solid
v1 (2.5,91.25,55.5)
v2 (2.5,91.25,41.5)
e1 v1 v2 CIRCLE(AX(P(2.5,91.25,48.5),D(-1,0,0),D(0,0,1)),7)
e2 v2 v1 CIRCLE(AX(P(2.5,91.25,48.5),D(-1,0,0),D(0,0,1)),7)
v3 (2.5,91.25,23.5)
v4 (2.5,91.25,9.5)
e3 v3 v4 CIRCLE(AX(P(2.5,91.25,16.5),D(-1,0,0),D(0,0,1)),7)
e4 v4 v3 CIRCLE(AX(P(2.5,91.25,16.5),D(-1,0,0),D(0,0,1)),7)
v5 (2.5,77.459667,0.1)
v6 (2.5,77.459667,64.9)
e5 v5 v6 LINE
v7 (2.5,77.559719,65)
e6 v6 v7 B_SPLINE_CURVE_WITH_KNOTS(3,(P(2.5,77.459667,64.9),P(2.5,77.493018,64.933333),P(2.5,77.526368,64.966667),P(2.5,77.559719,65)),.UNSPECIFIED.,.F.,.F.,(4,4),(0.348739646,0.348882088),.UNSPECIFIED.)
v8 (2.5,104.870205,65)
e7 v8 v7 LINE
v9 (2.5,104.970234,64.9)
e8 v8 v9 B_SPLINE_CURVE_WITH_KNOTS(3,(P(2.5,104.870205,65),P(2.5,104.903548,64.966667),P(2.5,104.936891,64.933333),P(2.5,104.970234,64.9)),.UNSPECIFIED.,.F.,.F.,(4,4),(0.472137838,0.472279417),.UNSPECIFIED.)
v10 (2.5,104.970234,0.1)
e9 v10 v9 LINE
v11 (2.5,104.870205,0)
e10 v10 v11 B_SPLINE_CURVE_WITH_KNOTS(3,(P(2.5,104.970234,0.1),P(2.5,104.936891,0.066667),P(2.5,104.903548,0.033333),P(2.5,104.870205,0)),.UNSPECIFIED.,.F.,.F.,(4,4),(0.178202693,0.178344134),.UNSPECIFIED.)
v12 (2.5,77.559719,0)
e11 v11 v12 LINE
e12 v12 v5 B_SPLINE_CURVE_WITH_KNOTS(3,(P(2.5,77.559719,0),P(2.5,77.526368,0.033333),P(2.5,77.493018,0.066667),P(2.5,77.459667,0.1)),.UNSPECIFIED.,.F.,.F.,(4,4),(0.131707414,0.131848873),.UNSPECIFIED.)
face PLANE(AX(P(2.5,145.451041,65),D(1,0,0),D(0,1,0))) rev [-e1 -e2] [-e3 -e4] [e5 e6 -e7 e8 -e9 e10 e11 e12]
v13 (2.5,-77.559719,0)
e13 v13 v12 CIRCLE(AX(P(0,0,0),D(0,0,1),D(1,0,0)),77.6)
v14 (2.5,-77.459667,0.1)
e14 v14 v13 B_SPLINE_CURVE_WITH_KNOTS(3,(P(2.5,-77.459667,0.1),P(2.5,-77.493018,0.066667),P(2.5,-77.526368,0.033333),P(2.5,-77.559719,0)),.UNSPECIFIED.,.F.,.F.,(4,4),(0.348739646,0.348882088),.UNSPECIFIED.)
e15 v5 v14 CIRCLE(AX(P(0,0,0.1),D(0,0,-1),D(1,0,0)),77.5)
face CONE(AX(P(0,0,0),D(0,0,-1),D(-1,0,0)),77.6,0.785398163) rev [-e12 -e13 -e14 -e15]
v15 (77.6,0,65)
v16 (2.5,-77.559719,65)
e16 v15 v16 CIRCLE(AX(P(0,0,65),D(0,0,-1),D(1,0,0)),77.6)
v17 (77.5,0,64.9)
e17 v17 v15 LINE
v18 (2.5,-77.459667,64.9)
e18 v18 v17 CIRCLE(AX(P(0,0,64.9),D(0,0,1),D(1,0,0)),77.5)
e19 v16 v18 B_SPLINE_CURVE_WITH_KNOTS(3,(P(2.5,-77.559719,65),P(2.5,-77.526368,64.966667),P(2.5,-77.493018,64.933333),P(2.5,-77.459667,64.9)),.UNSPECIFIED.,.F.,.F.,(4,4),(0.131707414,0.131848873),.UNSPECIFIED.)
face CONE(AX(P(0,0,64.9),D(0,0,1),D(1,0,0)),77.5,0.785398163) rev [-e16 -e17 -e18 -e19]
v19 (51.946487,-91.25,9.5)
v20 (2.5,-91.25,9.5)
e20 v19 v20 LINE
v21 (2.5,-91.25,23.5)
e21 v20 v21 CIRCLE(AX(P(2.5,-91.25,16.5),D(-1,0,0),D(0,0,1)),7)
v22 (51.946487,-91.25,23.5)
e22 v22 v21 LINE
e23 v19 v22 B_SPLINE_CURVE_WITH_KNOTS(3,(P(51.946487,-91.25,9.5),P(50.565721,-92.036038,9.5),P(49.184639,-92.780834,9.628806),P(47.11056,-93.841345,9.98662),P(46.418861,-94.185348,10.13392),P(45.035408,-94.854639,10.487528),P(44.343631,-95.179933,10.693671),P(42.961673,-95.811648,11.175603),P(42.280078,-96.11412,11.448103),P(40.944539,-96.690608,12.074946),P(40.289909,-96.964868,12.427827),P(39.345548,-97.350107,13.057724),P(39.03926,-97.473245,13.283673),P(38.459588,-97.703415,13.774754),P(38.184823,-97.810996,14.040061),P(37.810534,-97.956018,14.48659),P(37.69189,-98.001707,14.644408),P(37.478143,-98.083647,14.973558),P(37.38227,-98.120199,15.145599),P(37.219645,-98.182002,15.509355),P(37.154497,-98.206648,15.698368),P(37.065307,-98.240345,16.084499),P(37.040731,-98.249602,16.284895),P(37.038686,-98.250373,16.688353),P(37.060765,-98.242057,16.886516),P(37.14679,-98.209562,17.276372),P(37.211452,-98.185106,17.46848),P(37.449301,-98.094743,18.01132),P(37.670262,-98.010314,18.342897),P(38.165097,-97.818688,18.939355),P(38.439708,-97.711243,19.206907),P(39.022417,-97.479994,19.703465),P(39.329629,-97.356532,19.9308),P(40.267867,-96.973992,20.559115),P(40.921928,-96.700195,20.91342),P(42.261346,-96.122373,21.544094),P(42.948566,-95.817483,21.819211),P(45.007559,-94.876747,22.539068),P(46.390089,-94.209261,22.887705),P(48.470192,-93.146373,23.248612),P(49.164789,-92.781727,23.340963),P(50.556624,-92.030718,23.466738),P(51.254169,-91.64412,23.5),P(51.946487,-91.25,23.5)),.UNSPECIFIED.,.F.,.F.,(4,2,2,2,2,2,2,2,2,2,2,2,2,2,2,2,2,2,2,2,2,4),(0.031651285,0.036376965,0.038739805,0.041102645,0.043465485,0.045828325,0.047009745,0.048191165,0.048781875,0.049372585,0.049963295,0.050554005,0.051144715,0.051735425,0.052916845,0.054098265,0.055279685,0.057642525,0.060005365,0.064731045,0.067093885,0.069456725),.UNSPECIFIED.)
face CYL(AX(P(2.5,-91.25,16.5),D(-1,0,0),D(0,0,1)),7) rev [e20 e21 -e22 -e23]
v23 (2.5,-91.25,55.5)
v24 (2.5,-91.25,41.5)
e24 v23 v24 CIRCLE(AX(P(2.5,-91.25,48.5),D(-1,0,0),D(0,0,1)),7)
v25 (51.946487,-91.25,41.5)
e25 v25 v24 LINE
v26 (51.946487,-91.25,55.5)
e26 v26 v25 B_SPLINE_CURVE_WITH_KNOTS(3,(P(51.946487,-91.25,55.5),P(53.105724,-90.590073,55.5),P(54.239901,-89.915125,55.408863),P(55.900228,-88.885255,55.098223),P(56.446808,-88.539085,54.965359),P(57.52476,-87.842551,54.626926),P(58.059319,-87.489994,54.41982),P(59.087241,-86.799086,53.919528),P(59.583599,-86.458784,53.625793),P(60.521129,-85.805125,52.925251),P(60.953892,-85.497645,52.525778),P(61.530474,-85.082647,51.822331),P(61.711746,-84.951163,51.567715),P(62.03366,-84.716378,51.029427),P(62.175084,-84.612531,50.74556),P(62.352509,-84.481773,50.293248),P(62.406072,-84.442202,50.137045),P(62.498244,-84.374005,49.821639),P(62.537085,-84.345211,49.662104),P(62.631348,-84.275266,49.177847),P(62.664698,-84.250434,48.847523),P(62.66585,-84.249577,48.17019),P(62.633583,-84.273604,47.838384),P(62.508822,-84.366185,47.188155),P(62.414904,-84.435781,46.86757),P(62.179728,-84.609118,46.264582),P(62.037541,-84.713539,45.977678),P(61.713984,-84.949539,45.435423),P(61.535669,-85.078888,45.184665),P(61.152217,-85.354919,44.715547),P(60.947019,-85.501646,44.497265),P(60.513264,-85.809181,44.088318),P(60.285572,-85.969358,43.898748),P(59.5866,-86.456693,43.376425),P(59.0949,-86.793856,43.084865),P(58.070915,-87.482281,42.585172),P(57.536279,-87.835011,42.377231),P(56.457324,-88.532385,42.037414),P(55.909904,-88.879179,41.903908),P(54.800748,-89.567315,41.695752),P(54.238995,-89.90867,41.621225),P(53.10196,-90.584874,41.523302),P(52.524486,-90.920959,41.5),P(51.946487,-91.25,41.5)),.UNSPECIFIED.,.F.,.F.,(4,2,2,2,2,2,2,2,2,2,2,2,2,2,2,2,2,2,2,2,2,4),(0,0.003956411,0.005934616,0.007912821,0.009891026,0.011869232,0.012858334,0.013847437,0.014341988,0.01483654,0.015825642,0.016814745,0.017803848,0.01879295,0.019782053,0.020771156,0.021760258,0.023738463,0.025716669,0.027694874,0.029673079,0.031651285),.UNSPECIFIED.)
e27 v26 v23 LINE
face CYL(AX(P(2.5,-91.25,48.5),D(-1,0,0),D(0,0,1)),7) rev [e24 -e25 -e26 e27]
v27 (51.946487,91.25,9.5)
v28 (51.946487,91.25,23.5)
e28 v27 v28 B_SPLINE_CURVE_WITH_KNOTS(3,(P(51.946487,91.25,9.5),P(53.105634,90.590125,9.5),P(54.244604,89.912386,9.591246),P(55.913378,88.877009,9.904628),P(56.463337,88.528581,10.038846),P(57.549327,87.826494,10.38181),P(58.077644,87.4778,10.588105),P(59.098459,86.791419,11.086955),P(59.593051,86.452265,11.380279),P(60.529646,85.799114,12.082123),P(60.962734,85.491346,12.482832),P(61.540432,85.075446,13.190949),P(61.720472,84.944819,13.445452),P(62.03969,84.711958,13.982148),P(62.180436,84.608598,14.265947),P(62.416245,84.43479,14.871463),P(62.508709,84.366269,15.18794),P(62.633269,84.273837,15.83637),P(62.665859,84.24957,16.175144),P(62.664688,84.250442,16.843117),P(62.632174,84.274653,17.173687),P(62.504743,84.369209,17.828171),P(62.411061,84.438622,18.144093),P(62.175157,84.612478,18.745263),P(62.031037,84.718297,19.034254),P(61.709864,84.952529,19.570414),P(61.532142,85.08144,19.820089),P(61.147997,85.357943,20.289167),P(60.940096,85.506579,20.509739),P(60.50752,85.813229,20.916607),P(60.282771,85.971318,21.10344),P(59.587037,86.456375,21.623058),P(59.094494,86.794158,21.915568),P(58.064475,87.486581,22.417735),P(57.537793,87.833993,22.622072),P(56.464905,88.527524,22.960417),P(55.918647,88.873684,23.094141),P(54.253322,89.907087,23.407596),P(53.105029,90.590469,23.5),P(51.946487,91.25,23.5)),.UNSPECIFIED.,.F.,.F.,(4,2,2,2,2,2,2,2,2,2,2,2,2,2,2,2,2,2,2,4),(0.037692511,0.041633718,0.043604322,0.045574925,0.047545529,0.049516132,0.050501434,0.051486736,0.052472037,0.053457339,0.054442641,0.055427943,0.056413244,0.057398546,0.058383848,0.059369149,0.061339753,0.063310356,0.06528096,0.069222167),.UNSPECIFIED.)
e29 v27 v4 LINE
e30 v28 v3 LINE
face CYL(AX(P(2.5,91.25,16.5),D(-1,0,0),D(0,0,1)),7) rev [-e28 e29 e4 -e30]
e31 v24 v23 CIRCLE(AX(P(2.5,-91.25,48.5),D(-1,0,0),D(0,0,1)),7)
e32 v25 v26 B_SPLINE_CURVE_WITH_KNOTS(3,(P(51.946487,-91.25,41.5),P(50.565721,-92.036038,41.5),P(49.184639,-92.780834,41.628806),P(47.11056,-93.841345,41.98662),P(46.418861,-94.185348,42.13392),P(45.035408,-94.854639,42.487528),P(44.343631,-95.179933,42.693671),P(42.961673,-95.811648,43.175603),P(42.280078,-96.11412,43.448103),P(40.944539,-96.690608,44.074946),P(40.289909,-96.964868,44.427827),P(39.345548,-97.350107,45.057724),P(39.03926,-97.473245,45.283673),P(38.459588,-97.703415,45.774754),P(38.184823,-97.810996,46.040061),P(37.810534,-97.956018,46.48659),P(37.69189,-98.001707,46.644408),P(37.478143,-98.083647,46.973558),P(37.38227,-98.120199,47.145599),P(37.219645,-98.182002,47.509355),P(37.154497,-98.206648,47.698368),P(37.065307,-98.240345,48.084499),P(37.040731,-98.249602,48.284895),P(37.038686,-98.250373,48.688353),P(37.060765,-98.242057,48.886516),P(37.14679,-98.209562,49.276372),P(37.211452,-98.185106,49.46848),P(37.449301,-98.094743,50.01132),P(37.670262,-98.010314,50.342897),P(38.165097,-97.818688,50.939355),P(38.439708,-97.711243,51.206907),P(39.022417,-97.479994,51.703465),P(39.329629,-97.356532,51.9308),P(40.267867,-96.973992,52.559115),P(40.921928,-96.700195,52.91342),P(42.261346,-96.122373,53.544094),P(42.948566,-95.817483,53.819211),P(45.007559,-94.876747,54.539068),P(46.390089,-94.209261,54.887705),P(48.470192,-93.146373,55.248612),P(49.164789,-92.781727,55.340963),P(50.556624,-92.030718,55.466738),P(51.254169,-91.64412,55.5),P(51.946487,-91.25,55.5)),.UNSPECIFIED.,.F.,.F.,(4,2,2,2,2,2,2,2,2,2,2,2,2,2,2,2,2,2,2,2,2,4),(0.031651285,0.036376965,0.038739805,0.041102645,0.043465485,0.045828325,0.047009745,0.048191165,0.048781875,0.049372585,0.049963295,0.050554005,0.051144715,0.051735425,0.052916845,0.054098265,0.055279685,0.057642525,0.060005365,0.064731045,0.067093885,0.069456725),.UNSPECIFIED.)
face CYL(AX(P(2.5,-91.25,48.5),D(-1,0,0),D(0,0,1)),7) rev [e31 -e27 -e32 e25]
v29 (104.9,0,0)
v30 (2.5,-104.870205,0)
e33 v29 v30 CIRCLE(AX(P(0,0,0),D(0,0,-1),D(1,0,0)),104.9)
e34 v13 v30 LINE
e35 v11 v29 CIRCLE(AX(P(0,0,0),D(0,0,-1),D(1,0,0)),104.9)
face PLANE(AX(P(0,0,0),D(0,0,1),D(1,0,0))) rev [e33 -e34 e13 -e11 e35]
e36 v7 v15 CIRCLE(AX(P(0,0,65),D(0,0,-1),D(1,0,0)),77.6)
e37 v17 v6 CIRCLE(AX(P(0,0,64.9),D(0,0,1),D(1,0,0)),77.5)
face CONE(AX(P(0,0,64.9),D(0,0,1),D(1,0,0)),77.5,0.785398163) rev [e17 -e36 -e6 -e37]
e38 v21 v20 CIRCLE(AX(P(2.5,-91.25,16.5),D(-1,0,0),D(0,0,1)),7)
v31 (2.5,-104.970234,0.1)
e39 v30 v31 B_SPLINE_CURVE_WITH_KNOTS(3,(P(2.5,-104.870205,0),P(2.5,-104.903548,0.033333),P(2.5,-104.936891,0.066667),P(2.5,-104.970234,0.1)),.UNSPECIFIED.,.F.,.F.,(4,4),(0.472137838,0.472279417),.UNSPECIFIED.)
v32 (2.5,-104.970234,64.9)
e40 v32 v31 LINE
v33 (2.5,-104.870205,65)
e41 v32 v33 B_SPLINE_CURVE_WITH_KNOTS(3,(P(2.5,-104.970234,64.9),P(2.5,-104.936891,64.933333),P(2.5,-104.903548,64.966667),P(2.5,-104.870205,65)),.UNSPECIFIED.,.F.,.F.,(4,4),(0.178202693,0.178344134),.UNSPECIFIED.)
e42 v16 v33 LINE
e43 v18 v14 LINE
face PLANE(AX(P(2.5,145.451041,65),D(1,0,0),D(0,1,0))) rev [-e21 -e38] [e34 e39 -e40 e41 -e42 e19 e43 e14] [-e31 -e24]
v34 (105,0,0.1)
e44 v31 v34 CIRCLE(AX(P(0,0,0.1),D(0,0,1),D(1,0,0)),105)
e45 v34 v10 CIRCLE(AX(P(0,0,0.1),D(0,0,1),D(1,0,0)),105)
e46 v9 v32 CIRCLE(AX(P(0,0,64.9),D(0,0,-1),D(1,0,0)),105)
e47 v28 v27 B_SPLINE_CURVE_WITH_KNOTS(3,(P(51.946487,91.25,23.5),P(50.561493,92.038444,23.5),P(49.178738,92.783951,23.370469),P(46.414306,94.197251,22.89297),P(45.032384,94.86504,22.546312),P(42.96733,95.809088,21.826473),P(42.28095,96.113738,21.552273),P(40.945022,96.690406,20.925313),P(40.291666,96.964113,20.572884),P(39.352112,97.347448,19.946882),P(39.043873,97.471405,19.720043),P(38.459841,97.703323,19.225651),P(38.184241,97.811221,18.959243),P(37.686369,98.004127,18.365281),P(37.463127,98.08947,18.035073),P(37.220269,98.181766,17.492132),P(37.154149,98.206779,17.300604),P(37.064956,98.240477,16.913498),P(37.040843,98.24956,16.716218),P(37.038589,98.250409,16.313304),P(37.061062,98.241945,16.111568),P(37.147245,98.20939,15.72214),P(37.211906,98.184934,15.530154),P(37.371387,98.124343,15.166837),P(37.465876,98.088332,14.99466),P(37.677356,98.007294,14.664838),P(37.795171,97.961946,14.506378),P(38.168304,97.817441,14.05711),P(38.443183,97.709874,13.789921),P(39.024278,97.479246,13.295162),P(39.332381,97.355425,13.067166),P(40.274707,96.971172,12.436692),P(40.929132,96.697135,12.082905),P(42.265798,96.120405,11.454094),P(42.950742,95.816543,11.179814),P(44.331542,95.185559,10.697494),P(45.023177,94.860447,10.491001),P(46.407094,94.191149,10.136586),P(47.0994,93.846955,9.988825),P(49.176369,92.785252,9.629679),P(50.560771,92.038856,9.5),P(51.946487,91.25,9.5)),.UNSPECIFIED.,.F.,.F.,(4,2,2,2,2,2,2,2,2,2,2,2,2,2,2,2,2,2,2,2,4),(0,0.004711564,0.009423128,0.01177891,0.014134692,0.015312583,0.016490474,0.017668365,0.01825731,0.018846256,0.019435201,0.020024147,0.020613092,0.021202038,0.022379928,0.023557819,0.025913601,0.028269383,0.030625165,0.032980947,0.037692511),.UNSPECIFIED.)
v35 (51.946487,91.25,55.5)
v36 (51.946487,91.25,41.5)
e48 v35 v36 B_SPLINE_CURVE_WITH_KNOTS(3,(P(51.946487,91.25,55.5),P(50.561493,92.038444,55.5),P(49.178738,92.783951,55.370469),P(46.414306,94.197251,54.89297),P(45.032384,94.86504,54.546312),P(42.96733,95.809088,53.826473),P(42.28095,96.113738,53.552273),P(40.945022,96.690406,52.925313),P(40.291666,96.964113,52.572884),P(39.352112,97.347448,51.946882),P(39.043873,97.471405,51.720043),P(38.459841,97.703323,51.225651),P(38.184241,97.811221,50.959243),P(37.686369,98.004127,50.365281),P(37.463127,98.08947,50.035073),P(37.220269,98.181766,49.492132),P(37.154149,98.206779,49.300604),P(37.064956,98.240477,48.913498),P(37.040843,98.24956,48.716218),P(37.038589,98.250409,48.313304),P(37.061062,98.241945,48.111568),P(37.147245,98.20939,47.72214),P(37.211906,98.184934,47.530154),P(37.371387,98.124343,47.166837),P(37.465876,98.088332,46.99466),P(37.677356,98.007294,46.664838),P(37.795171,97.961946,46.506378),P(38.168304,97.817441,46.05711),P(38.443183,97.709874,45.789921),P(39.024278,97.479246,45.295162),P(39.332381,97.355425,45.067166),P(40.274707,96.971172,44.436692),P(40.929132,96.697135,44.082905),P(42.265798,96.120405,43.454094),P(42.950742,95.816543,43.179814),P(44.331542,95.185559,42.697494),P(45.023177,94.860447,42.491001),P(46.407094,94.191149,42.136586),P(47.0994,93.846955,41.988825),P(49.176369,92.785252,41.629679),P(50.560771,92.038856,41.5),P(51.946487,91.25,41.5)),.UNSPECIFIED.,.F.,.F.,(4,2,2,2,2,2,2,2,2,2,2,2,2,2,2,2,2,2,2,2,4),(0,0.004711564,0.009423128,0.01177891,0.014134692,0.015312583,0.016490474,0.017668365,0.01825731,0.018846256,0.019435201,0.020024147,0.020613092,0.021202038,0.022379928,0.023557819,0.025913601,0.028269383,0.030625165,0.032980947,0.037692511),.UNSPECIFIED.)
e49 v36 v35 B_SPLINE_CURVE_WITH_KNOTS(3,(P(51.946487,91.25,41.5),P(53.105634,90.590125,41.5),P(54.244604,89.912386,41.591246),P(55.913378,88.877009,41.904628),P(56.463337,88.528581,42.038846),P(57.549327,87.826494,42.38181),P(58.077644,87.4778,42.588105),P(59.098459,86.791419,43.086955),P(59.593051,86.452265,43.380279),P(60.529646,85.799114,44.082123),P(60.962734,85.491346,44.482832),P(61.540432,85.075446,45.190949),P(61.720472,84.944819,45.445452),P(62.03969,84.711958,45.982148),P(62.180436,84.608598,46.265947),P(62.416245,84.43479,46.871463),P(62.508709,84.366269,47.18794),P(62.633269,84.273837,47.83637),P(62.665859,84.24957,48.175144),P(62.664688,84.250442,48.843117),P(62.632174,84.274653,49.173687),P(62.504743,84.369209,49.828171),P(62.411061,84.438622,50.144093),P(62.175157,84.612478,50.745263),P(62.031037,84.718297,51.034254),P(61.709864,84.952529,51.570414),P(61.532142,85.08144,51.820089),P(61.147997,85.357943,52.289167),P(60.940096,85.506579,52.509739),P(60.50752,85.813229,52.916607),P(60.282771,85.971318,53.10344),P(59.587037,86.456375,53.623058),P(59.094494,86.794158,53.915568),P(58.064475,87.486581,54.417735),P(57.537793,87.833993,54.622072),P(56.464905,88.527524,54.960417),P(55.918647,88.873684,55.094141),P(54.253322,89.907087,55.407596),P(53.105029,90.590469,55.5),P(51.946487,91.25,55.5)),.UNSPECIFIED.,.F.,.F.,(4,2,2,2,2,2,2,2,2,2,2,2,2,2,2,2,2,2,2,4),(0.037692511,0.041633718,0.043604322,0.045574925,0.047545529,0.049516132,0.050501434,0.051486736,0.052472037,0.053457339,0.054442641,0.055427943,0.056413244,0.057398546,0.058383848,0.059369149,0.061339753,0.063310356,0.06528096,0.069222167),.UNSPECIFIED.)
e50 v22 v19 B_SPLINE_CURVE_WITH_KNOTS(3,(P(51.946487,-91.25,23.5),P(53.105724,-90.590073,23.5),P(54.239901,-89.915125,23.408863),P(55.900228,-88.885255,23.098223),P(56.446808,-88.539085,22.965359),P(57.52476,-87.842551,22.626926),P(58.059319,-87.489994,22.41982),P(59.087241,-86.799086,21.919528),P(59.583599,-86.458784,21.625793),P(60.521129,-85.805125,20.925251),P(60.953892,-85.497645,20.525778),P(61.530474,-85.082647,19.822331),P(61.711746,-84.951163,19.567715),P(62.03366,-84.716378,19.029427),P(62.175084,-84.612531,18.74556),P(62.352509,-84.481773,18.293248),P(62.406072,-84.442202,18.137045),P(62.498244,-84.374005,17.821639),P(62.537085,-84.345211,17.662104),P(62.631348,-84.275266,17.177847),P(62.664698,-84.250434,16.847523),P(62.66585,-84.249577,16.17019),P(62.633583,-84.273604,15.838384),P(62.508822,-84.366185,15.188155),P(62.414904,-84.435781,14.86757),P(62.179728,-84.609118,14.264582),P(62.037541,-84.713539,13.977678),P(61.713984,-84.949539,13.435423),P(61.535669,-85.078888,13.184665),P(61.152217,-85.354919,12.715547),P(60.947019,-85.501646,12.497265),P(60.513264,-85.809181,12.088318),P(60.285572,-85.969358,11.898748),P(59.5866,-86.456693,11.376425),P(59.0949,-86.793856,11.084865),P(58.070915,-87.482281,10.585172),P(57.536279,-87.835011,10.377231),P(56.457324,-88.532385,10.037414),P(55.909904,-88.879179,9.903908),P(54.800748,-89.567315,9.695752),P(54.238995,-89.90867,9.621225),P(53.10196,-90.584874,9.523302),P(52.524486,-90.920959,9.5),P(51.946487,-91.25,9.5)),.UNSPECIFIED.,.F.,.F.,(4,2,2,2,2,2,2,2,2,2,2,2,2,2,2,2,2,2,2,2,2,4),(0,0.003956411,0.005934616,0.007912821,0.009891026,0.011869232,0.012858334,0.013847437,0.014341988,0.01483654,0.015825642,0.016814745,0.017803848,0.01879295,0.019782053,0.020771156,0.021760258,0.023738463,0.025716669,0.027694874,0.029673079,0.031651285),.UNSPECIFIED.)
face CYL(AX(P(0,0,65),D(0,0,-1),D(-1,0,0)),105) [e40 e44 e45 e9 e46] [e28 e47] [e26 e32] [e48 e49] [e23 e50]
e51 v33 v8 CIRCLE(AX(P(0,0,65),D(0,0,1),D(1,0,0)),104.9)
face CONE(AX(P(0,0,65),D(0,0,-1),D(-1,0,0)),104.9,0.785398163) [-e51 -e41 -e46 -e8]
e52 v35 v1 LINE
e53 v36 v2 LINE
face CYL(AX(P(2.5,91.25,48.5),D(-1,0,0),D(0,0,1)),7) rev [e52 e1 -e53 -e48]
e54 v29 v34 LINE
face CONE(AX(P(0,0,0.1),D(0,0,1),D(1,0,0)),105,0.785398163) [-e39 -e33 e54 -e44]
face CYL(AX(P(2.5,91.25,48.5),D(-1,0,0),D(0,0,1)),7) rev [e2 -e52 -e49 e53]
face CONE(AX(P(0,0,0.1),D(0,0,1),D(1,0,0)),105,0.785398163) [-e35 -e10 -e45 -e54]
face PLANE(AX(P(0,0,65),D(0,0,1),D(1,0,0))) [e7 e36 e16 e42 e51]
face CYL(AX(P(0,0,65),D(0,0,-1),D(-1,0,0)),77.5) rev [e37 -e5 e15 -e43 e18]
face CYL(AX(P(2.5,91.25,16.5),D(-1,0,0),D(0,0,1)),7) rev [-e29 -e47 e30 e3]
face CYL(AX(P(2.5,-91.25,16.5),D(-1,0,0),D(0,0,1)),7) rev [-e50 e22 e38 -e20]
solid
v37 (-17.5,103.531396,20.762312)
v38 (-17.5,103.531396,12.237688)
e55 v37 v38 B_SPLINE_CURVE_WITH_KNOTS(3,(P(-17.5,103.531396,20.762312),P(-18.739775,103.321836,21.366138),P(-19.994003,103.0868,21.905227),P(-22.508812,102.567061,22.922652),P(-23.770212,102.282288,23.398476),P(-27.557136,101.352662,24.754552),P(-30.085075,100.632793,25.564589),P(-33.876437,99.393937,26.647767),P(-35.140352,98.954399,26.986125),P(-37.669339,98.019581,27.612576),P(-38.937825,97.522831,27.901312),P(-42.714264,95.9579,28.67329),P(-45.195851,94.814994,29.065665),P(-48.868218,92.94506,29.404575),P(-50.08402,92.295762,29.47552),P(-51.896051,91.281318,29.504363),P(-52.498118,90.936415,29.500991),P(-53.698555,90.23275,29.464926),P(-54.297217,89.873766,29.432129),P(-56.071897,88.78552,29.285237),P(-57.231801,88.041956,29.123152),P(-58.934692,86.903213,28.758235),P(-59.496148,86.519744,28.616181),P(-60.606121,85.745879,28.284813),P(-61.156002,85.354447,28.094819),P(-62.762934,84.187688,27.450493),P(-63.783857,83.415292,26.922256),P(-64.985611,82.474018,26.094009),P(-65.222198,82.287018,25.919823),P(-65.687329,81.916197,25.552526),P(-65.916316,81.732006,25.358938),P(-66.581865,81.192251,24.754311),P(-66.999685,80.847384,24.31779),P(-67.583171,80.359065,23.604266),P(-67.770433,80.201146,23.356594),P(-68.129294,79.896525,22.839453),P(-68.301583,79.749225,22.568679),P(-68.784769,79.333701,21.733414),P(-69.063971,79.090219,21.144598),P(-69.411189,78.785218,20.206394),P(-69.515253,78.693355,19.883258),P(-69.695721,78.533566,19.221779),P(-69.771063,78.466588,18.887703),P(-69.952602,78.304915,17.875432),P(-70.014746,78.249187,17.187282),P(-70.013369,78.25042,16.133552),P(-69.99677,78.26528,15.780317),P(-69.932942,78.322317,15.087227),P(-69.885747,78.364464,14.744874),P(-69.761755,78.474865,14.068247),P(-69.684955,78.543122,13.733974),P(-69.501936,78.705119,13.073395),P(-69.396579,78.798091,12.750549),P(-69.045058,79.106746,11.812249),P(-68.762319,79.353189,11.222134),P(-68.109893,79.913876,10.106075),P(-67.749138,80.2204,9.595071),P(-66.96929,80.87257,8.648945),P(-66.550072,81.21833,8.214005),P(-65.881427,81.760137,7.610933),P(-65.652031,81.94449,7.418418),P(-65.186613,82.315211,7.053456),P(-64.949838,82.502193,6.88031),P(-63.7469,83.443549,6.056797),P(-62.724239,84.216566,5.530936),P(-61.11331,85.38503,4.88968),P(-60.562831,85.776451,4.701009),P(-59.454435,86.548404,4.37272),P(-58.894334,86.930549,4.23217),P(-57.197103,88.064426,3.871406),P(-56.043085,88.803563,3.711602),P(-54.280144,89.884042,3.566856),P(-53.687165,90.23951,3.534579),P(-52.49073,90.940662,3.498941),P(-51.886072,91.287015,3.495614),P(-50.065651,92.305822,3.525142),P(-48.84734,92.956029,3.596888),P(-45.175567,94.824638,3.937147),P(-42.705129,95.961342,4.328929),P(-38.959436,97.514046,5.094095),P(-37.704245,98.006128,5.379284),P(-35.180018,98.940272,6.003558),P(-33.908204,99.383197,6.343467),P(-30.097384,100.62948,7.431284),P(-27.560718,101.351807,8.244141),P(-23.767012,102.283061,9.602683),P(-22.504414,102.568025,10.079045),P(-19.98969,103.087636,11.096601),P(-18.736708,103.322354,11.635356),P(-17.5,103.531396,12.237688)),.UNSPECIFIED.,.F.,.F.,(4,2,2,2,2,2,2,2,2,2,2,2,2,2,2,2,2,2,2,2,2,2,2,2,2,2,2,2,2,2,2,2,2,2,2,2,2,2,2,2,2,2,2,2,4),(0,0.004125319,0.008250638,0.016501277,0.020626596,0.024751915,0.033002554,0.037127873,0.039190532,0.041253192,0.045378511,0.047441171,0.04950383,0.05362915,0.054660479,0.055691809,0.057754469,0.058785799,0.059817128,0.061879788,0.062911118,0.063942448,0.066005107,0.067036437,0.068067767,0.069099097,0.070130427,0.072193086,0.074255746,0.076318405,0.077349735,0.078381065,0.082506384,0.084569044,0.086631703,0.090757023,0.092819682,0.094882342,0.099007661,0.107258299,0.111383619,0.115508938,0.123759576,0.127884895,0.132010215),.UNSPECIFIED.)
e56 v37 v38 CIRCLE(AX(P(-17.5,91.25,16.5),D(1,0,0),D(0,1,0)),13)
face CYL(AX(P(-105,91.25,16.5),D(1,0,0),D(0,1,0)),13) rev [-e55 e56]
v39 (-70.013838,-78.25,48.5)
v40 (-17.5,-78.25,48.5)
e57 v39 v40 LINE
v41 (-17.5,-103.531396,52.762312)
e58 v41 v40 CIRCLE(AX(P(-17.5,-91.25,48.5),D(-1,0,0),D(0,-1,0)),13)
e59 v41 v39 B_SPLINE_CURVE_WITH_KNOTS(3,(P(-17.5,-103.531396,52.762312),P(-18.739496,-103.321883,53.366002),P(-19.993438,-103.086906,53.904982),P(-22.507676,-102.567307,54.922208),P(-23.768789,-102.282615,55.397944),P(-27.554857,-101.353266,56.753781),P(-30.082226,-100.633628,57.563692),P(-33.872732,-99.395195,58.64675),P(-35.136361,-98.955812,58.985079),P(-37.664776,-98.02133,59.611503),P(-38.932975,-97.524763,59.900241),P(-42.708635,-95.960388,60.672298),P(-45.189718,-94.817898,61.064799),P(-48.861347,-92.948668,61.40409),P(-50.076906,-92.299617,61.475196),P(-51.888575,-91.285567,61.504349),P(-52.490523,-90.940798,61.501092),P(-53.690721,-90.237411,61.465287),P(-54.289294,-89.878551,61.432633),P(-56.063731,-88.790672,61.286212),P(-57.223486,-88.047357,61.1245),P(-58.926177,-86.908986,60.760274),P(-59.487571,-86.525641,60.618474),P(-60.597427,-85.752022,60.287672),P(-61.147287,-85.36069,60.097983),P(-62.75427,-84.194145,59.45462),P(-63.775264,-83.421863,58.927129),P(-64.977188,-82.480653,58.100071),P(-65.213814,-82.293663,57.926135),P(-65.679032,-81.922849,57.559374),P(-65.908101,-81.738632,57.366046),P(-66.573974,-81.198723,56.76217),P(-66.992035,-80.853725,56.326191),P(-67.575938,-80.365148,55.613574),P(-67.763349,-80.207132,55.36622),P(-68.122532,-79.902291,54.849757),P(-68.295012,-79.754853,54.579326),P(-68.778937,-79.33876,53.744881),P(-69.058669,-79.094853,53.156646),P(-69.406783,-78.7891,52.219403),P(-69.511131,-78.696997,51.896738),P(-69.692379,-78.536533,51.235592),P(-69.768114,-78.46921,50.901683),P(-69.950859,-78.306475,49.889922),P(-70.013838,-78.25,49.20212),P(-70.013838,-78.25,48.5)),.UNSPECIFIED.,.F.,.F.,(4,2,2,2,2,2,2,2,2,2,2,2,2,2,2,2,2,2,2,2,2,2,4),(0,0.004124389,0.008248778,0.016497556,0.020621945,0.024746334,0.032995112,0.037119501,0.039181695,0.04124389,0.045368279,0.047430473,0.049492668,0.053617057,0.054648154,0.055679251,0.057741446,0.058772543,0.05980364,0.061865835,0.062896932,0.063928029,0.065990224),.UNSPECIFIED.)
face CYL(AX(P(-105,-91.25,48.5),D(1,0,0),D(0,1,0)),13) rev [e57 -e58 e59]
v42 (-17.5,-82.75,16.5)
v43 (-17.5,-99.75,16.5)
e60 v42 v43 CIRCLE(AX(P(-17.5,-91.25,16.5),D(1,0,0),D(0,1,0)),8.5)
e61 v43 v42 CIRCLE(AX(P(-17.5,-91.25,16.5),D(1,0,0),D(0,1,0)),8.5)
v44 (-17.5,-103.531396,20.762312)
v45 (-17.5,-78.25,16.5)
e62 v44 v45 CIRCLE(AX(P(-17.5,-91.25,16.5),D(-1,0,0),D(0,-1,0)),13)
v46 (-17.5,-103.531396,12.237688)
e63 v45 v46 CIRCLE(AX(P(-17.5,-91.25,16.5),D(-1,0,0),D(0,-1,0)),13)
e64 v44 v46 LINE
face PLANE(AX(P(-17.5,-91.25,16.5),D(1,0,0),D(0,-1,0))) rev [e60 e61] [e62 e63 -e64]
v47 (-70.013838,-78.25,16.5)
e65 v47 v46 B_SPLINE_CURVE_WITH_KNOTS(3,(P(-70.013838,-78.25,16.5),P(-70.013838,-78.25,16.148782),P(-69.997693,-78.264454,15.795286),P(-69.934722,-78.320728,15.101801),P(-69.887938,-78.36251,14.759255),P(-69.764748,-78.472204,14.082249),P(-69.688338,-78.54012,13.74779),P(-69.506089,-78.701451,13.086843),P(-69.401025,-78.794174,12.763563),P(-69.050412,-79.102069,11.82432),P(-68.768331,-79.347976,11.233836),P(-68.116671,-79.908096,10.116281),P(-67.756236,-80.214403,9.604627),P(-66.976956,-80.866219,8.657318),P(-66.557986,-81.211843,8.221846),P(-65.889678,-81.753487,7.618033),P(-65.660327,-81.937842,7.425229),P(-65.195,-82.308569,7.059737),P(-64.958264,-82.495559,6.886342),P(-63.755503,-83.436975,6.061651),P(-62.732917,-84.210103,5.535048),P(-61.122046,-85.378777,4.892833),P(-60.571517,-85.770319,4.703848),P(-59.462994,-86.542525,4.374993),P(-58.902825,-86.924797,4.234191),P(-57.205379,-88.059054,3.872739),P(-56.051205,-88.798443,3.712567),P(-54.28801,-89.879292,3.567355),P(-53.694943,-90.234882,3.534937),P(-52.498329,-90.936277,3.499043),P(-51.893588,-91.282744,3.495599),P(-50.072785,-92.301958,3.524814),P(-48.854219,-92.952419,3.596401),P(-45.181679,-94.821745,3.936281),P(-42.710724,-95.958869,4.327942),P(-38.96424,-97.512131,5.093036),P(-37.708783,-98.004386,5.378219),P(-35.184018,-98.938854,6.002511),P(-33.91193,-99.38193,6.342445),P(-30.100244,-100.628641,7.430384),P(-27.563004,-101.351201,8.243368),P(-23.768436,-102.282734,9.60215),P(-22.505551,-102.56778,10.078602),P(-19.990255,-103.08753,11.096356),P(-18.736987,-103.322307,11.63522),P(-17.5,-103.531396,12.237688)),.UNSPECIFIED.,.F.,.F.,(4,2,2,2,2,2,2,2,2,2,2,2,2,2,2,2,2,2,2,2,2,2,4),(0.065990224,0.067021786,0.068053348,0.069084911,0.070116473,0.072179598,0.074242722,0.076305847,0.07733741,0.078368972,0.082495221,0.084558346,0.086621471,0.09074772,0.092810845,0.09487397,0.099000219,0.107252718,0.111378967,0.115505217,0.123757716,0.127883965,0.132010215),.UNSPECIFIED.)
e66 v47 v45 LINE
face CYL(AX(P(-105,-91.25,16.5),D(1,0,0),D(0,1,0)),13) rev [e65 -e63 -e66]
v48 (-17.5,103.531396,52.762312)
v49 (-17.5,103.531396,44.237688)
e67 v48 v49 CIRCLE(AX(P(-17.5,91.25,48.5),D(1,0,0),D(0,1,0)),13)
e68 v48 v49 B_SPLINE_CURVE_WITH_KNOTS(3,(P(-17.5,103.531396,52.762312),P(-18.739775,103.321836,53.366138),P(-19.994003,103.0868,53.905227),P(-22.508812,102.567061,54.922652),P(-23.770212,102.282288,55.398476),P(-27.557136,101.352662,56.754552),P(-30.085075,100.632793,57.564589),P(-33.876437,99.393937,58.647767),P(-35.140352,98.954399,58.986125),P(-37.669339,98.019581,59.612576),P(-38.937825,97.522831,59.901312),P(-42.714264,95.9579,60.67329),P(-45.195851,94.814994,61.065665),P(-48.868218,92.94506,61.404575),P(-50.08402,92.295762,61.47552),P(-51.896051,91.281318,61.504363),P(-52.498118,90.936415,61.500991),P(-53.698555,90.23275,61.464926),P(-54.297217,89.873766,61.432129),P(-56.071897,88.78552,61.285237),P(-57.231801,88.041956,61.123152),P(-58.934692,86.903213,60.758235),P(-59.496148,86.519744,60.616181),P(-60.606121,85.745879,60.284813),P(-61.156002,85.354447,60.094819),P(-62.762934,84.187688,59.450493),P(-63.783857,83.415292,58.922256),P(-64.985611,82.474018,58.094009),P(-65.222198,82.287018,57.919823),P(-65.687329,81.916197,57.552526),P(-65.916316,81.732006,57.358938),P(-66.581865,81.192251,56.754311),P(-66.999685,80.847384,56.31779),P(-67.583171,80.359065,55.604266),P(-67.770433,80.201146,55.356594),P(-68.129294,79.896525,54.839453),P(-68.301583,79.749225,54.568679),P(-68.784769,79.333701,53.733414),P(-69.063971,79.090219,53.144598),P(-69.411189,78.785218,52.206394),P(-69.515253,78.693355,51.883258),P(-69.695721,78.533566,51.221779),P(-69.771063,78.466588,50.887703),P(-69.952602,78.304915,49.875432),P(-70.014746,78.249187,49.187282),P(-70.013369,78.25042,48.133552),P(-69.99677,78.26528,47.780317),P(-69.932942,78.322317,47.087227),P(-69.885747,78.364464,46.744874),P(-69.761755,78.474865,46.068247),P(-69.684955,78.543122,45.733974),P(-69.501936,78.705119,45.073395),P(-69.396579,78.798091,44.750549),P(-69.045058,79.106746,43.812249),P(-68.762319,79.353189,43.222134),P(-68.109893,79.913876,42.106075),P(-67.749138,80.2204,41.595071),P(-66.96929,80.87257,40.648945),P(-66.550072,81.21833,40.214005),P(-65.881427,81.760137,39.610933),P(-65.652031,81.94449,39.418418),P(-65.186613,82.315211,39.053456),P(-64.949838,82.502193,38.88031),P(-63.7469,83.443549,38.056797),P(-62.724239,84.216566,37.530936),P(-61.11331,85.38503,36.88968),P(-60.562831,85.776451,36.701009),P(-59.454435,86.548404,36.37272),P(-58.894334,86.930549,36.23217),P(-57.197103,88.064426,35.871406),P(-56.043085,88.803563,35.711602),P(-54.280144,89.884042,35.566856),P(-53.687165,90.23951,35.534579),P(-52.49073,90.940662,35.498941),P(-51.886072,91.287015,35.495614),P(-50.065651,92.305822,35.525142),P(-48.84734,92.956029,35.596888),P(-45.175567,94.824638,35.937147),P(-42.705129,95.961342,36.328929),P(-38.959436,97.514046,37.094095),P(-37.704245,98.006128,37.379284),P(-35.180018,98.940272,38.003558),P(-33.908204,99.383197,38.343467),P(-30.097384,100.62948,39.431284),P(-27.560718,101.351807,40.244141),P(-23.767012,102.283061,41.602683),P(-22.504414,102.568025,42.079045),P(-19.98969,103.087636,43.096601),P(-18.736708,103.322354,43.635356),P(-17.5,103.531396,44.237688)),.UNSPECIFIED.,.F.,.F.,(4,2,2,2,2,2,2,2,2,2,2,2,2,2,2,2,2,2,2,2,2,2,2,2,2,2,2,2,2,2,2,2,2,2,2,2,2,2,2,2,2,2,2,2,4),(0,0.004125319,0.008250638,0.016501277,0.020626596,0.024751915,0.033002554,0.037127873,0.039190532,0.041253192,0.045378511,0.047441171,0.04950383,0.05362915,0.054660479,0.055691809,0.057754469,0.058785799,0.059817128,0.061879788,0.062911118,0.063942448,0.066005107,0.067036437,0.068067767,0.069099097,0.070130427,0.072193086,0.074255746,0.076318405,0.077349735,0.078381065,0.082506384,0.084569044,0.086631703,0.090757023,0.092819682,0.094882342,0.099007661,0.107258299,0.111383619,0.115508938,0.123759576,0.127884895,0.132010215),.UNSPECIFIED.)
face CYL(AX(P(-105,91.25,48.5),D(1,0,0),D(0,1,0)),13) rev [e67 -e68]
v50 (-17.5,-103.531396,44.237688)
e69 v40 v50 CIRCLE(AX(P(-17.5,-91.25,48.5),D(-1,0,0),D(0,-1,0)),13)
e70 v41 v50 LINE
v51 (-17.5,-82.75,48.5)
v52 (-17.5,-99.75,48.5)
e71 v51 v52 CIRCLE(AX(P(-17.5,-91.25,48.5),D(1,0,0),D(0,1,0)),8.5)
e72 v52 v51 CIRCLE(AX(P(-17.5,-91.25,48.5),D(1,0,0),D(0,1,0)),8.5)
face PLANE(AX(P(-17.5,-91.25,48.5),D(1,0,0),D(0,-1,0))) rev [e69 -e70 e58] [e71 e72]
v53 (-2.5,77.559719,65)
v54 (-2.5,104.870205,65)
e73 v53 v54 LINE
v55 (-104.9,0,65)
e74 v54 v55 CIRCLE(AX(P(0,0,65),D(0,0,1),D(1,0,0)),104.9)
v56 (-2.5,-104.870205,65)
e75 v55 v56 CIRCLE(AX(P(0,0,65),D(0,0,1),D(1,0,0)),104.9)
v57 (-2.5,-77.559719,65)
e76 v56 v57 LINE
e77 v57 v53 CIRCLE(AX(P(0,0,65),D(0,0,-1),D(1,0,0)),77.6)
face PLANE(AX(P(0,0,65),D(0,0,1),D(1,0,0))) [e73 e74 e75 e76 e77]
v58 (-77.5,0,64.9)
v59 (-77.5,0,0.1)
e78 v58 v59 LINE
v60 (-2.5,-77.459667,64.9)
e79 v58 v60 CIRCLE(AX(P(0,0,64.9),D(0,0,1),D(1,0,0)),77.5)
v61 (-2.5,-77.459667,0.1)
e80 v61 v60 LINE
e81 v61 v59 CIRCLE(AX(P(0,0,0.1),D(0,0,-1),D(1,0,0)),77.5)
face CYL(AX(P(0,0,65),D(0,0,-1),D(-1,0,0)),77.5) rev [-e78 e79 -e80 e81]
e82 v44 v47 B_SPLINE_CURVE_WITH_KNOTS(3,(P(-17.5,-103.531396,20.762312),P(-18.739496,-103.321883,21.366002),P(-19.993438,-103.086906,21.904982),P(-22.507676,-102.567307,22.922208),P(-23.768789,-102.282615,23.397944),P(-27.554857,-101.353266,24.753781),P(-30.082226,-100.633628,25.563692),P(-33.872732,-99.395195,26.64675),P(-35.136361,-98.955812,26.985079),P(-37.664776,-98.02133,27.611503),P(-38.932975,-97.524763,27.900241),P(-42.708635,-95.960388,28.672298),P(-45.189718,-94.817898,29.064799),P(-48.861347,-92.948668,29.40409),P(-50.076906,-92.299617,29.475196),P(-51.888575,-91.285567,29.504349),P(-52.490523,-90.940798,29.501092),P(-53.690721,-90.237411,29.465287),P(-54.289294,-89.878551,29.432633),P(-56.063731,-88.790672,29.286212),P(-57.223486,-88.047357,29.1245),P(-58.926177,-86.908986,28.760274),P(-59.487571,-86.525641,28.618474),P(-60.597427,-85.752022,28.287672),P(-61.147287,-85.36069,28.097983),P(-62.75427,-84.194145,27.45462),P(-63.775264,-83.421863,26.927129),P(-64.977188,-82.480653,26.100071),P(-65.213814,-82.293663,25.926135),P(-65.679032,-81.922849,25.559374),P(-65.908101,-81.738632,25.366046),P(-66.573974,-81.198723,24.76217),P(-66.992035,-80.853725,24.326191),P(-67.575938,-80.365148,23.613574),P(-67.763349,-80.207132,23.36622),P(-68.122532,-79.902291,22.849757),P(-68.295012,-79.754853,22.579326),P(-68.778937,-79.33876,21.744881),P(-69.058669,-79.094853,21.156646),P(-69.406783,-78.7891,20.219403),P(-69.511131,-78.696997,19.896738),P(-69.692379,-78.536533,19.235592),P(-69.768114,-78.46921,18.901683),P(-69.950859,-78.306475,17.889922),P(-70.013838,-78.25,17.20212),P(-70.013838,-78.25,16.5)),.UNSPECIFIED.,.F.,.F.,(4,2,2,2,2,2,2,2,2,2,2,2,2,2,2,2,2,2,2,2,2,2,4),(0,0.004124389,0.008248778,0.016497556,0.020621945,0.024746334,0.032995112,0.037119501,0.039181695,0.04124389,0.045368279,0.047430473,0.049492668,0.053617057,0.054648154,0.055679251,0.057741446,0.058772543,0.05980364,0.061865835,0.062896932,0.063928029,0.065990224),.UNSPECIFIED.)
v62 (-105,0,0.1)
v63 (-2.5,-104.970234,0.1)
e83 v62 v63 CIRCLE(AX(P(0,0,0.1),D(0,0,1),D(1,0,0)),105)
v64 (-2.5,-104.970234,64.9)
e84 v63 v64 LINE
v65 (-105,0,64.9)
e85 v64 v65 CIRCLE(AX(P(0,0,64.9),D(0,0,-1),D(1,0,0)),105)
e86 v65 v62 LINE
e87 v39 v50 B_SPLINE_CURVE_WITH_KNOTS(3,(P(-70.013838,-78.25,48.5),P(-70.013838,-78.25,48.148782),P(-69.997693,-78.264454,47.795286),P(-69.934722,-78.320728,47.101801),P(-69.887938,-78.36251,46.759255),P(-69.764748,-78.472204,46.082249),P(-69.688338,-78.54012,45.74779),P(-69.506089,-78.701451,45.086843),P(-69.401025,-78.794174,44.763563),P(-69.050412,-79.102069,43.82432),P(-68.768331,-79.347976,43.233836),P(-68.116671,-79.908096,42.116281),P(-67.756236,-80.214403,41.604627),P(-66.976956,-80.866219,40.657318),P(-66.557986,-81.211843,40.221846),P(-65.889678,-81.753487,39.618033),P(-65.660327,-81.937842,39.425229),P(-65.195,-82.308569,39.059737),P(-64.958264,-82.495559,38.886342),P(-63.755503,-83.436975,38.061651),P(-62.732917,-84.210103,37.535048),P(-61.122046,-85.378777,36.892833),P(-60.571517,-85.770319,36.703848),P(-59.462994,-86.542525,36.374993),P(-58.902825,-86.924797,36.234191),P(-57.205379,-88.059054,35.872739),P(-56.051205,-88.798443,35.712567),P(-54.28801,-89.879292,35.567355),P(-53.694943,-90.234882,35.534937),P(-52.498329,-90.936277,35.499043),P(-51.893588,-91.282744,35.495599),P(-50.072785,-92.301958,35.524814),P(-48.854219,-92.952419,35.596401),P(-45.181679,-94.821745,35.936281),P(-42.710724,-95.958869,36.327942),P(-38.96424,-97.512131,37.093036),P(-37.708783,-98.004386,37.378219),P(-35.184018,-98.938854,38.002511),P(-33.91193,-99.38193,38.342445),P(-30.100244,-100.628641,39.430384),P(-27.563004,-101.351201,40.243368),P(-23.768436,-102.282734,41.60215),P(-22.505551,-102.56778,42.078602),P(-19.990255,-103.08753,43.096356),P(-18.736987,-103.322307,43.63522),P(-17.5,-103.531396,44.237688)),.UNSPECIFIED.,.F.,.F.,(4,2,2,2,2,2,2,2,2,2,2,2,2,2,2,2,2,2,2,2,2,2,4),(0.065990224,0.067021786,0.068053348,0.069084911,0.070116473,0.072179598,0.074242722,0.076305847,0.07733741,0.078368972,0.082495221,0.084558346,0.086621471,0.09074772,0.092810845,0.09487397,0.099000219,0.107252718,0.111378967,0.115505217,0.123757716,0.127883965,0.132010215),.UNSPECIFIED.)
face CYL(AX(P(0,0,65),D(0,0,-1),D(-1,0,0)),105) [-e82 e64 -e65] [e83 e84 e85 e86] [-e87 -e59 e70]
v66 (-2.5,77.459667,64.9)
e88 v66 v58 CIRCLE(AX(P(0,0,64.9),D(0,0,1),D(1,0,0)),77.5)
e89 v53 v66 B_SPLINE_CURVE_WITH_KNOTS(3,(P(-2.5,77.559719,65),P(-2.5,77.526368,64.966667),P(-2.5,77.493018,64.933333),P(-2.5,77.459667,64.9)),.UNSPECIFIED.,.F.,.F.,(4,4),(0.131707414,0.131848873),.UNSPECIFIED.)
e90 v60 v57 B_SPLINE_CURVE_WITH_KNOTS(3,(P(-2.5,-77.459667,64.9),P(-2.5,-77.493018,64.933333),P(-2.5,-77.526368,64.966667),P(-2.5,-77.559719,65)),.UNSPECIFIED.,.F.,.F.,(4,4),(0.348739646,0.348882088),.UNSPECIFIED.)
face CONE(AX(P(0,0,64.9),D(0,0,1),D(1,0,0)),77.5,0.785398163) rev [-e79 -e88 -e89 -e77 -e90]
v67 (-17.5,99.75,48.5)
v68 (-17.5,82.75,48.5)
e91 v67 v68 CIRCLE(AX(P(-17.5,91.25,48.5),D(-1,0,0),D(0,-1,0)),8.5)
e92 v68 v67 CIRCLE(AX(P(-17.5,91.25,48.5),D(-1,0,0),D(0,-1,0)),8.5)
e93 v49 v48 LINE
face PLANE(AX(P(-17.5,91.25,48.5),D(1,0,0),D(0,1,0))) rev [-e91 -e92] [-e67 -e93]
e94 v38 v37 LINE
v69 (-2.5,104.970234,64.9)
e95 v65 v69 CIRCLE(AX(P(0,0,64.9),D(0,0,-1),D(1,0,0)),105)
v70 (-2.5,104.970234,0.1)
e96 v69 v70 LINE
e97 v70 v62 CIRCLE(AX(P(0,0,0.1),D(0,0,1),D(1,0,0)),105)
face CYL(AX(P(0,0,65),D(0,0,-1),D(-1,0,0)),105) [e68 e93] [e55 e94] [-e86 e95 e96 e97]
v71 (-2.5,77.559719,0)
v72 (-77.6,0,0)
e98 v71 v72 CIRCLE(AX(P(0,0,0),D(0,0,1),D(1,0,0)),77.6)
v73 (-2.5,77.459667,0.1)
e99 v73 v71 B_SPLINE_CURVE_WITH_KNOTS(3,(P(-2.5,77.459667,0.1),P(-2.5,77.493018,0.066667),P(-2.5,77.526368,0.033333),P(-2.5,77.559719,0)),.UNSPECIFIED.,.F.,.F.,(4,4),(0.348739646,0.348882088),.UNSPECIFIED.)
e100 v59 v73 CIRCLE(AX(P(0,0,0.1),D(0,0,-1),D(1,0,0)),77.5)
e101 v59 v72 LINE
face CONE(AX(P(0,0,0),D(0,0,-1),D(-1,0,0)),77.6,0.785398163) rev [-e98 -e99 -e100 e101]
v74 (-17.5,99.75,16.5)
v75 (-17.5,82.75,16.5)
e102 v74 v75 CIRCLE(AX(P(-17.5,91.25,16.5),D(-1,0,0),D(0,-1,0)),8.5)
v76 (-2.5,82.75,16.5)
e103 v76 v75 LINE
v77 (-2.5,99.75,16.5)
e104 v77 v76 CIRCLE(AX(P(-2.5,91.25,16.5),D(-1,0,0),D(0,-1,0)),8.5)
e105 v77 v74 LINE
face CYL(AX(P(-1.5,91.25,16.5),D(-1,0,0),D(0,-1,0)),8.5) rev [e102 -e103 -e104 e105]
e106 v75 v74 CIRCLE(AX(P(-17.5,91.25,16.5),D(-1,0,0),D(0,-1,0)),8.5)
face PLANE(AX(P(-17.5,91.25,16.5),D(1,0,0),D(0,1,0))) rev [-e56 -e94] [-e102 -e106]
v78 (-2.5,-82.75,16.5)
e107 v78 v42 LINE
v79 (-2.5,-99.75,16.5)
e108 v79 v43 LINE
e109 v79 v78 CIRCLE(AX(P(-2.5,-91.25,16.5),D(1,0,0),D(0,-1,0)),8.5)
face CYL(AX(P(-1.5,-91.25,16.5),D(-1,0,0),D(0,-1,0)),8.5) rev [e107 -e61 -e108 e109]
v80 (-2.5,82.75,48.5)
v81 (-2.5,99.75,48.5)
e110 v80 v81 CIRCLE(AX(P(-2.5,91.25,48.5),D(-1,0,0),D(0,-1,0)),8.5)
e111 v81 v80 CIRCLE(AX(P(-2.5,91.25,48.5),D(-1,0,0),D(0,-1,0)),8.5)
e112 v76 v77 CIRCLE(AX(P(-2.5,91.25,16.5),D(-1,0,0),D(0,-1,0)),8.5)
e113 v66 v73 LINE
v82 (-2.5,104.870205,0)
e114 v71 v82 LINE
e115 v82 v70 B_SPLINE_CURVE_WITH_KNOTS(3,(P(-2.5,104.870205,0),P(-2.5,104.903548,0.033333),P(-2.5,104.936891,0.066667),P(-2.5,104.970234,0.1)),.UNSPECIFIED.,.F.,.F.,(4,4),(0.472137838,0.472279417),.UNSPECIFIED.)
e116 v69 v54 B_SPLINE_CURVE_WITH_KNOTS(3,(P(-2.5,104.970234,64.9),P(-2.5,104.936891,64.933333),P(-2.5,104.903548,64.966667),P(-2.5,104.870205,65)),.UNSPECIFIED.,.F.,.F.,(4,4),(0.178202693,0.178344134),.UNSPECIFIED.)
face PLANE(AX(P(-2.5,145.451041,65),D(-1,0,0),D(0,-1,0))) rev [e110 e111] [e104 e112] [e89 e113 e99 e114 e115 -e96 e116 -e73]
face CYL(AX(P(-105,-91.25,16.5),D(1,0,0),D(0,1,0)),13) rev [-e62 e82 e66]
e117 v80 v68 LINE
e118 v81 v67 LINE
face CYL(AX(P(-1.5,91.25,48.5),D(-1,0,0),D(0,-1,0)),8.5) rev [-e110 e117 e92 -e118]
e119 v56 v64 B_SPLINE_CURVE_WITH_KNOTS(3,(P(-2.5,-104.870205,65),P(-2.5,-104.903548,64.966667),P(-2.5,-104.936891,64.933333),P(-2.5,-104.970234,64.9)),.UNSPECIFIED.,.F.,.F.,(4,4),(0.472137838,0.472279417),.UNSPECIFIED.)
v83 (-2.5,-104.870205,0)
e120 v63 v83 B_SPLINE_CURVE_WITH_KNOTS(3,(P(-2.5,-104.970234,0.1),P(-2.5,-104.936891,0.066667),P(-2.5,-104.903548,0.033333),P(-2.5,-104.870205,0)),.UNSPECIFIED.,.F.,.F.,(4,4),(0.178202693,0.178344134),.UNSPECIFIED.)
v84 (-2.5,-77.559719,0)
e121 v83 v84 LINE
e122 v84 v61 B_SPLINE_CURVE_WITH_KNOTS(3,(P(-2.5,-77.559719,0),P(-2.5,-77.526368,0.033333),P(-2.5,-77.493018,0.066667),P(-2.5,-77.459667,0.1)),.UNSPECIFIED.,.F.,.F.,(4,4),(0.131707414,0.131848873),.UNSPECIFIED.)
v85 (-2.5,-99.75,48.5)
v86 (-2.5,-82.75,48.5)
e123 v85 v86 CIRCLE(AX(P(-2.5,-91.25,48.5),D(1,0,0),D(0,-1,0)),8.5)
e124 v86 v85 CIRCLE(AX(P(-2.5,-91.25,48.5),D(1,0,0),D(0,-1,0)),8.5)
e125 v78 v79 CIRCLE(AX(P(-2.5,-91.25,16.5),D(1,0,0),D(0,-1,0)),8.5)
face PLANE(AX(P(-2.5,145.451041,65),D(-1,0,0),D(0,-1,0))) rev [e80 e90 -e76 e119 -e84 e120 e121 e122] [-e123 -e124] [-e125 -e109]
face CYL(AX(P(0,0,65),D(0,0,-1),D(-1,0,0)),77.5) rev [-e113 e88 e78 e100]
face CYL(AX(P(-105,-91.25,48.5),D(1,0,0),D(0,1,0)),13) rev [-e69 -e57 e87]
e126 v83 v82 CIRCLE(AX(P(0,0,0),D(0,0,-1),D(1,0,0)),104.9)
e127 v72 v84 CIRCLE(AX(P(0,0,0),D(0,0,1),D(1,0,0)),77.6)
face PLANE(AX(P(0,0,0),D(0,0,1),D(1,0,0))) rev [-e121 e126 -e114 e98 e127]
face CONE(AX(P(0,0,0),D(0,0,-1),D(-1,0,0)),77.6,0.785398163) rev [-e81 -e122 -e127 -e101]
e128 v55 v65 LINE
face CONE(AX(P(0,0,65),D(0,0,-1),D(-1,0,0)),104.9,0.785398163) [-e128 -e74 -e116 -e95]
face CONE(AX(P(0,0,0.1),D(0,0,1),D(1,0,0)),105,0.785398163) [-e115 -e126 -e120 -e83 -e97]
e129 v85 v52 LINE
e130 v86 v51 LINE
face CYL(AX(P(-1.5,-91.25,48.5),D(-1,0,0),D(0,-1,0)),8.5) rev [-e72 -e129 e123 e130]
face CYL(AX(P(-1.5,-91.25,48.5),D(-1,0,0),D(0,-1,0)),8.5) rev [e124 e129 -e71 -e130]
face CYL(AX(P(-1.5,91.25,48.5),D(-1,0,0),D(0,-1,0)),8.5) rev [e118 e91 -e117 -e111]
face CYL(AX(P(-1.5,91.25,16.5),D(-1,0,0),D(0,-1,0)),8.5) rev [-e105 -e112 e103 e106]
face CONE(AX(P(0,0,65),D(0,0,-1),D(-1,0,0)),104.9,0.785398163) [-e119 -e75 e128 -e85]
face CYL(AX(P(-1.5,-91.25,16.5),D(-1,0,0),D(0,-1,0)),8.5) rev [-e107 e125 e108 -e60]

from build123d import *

# Parameters (mm, degrees)
SKETCH1_R                   = 105
SKETCH1_R_2                 = 77.5
BOSS_EXTRUDE1_DEPTH         = 65
CHAMFER1_SIZE               = 0.1
SKETCH2_W                   = 5
SKETCH2_H                   = 290.90208271
CUT_EXTRUDE1_DEPTH          = 163.095650774
CUT_EXTRUDE2_START          = -15
SKETCH3_R                   = 13
CUT_EXTRUDE2_DEPTH          = 149.707055437
SKETCH4_R                   = 8.5
CUT_EXTRUDE3_DEPTH          = 16
SKETCH7_W                   = 7
SKETCH7_H                   = 102.5
M16_TAPPED_HOLE1_AT_2_COUNT = 2
M16_TAPPED_HOLE1_AT_2_PITCH = 32
MIRROR1_COPY_1_SKETCH_W     = 7
MIRROR1_COPY_1_SKETCH_H     = 102.5


with BuildPart() as part:
    # Sketch1 → Boss-Extrude1 (new body)
    with BuildSketch(Plane.XY):
        Circle(SKETCH1_R)
        Circle(SKETCH1_R_2, mode=Mode.SUBTRACT)
    extrude(amount=BOSS_EXTRUDE1_DEPTH)

    # Chamfer1
    chamfer1_edges = [part.edges().sort_by_distance(p)[0] for p in [
        (-105, 0, 0),
        (-105, 0, 65),
        (-77.5, 0, 0),
        (-77.5, 0, 65),
    ]]
    chamfer(chamfer1_edges, length=CHAMFER1_SIZE)

    # Sketch2 → Cut-Extrude1 (cut, through all)
    with BuildSketch(Plane(origin=(0, 0, 0), x_dir=(-1, 0, 0), z_dir=(0, 0, -1))):
        Rectangle(SKETCH2_W, SKETCH2_H)
    extrude(amount=-CUT_EXTRUDE1_DEPTH, mode=Mode.SUBTRACT)


with BuildPart() as cut_extrude1_piece_1:
    # of the separate pieces the step leaves, piece 1, a body of its own (cut_extrude1_pieces)
    add(part.part.solids().sort_by_distance((2.5, -104.970233876, 0.1))[0])

    # Sketch7 → M16 Tapped Hole1 (revolve, cut)
    with BuildSketch(Plane(origin=(2.5, 91.25, 48.5), x_dir=(0, 0, 1), z_dir=(0, 1, 0))):
        with Locations((3.5, 51.25)):
            Rectangle(SKETCH7_W, SKETCH7_H)
    m16_tapped_hole1 = revolve(axis=Axis((-3.85, 91.25, 48.5), (1, 0, 0)), mode=Mode.SUBTRACT)

    # M16 Tapped Hole1 at 2: M16 Tapped Hole1 ×2
    with Locations(*[(0, 0, -i * M16_TAPPED_HOLE1_AT_2_PITCH) for i in range(1, M16_TAPPED_HOLE1_AT_2_COUNT)]):
        add(m16_tapped_hole1, mode=Mode.SUBTRACT)

    # Mirror1: M16 Tapped Hole1 across plane
    add(m16_tapped_hole1.mirror(Plane.ZX), mode=Mode.SUBTRACT)

    # Mirror1 copy 1 sketch → Mirror1 copy 1 (revolve, cut)
    with BuildSketch(Plane(origin=(2.5, -91.25, 16.5), x_dir=(0, 0, 1), z_dir=(0, -1, 0))):
        with Locations((3.5, -51.25)):
            Rectangle(MIRROR1_COPY_1_SKETCH_W, MIRROR1_COPY_1_SKETCH_H)
    revolve(axis=Axis((-3.85, -91.25, 16.5), (-1, 0, 0)), mode=Mode.SUBTRACT)


with BuildPart() as cut_extrude1_piece_2:
    # of the separate pieces the step leaves, piece 2, a body of its own (cut_extrude1_pieces)
    add(part.part.solids().sort_by_distance((-2.5, 104.970233876, 0.1))[0])

    # Sketch3 → Cut-Extrude2 (cut, through all)
    with BuildSketch(Plane(origin=(-2.5, 0, 0), x_dir=(0, 0, -1), z_dir=(1, 0, 0)).offset(CUT_EXTRUDE2_START)):
        with Locations((-48.5, 91.25)):
            Circle(SKETCH3_R)
        with Locations((-16.5, 91.25)):
            Circle(SKETCH3_R)
    cut_extrude2 = extrude(amount=-CUT_EXTRUDE2_DEPTH, mode=Mode.SUBTRACT)

    # Sketch4 → Cut-Extrude3 (cut)
    with BuildSketch(Plane.ZY.offset(17.5)):
        with Locations(Location((48.5, 91.25, 0), (0, 0, 270))):
            Circle(SKETCH4_R)
        with Locations(Location((16.5, 91.25, 0), (0, 0, 270))):
            Circle(SKETCH4_R)
    cut_extrude3 = extrude(amount=-CUT_EXTRUDE3_DEPTH, mode=Mode.SUBTRACT)

    # Mirror2: Cut-Extrude2 across plane
    add(cut_extrude2.mirror(Plane.ZX), mode=Mode.SUBTRACT)

    # Mirror3: Cut-Extrude3 across plane
    add(cut_extrude3.mirror(Plane.ZX), mode=Mode.SUBTRACT)


solid = Compound([cut_extrude1_piece_1.part, cut_extrude1_piece_2.part])
